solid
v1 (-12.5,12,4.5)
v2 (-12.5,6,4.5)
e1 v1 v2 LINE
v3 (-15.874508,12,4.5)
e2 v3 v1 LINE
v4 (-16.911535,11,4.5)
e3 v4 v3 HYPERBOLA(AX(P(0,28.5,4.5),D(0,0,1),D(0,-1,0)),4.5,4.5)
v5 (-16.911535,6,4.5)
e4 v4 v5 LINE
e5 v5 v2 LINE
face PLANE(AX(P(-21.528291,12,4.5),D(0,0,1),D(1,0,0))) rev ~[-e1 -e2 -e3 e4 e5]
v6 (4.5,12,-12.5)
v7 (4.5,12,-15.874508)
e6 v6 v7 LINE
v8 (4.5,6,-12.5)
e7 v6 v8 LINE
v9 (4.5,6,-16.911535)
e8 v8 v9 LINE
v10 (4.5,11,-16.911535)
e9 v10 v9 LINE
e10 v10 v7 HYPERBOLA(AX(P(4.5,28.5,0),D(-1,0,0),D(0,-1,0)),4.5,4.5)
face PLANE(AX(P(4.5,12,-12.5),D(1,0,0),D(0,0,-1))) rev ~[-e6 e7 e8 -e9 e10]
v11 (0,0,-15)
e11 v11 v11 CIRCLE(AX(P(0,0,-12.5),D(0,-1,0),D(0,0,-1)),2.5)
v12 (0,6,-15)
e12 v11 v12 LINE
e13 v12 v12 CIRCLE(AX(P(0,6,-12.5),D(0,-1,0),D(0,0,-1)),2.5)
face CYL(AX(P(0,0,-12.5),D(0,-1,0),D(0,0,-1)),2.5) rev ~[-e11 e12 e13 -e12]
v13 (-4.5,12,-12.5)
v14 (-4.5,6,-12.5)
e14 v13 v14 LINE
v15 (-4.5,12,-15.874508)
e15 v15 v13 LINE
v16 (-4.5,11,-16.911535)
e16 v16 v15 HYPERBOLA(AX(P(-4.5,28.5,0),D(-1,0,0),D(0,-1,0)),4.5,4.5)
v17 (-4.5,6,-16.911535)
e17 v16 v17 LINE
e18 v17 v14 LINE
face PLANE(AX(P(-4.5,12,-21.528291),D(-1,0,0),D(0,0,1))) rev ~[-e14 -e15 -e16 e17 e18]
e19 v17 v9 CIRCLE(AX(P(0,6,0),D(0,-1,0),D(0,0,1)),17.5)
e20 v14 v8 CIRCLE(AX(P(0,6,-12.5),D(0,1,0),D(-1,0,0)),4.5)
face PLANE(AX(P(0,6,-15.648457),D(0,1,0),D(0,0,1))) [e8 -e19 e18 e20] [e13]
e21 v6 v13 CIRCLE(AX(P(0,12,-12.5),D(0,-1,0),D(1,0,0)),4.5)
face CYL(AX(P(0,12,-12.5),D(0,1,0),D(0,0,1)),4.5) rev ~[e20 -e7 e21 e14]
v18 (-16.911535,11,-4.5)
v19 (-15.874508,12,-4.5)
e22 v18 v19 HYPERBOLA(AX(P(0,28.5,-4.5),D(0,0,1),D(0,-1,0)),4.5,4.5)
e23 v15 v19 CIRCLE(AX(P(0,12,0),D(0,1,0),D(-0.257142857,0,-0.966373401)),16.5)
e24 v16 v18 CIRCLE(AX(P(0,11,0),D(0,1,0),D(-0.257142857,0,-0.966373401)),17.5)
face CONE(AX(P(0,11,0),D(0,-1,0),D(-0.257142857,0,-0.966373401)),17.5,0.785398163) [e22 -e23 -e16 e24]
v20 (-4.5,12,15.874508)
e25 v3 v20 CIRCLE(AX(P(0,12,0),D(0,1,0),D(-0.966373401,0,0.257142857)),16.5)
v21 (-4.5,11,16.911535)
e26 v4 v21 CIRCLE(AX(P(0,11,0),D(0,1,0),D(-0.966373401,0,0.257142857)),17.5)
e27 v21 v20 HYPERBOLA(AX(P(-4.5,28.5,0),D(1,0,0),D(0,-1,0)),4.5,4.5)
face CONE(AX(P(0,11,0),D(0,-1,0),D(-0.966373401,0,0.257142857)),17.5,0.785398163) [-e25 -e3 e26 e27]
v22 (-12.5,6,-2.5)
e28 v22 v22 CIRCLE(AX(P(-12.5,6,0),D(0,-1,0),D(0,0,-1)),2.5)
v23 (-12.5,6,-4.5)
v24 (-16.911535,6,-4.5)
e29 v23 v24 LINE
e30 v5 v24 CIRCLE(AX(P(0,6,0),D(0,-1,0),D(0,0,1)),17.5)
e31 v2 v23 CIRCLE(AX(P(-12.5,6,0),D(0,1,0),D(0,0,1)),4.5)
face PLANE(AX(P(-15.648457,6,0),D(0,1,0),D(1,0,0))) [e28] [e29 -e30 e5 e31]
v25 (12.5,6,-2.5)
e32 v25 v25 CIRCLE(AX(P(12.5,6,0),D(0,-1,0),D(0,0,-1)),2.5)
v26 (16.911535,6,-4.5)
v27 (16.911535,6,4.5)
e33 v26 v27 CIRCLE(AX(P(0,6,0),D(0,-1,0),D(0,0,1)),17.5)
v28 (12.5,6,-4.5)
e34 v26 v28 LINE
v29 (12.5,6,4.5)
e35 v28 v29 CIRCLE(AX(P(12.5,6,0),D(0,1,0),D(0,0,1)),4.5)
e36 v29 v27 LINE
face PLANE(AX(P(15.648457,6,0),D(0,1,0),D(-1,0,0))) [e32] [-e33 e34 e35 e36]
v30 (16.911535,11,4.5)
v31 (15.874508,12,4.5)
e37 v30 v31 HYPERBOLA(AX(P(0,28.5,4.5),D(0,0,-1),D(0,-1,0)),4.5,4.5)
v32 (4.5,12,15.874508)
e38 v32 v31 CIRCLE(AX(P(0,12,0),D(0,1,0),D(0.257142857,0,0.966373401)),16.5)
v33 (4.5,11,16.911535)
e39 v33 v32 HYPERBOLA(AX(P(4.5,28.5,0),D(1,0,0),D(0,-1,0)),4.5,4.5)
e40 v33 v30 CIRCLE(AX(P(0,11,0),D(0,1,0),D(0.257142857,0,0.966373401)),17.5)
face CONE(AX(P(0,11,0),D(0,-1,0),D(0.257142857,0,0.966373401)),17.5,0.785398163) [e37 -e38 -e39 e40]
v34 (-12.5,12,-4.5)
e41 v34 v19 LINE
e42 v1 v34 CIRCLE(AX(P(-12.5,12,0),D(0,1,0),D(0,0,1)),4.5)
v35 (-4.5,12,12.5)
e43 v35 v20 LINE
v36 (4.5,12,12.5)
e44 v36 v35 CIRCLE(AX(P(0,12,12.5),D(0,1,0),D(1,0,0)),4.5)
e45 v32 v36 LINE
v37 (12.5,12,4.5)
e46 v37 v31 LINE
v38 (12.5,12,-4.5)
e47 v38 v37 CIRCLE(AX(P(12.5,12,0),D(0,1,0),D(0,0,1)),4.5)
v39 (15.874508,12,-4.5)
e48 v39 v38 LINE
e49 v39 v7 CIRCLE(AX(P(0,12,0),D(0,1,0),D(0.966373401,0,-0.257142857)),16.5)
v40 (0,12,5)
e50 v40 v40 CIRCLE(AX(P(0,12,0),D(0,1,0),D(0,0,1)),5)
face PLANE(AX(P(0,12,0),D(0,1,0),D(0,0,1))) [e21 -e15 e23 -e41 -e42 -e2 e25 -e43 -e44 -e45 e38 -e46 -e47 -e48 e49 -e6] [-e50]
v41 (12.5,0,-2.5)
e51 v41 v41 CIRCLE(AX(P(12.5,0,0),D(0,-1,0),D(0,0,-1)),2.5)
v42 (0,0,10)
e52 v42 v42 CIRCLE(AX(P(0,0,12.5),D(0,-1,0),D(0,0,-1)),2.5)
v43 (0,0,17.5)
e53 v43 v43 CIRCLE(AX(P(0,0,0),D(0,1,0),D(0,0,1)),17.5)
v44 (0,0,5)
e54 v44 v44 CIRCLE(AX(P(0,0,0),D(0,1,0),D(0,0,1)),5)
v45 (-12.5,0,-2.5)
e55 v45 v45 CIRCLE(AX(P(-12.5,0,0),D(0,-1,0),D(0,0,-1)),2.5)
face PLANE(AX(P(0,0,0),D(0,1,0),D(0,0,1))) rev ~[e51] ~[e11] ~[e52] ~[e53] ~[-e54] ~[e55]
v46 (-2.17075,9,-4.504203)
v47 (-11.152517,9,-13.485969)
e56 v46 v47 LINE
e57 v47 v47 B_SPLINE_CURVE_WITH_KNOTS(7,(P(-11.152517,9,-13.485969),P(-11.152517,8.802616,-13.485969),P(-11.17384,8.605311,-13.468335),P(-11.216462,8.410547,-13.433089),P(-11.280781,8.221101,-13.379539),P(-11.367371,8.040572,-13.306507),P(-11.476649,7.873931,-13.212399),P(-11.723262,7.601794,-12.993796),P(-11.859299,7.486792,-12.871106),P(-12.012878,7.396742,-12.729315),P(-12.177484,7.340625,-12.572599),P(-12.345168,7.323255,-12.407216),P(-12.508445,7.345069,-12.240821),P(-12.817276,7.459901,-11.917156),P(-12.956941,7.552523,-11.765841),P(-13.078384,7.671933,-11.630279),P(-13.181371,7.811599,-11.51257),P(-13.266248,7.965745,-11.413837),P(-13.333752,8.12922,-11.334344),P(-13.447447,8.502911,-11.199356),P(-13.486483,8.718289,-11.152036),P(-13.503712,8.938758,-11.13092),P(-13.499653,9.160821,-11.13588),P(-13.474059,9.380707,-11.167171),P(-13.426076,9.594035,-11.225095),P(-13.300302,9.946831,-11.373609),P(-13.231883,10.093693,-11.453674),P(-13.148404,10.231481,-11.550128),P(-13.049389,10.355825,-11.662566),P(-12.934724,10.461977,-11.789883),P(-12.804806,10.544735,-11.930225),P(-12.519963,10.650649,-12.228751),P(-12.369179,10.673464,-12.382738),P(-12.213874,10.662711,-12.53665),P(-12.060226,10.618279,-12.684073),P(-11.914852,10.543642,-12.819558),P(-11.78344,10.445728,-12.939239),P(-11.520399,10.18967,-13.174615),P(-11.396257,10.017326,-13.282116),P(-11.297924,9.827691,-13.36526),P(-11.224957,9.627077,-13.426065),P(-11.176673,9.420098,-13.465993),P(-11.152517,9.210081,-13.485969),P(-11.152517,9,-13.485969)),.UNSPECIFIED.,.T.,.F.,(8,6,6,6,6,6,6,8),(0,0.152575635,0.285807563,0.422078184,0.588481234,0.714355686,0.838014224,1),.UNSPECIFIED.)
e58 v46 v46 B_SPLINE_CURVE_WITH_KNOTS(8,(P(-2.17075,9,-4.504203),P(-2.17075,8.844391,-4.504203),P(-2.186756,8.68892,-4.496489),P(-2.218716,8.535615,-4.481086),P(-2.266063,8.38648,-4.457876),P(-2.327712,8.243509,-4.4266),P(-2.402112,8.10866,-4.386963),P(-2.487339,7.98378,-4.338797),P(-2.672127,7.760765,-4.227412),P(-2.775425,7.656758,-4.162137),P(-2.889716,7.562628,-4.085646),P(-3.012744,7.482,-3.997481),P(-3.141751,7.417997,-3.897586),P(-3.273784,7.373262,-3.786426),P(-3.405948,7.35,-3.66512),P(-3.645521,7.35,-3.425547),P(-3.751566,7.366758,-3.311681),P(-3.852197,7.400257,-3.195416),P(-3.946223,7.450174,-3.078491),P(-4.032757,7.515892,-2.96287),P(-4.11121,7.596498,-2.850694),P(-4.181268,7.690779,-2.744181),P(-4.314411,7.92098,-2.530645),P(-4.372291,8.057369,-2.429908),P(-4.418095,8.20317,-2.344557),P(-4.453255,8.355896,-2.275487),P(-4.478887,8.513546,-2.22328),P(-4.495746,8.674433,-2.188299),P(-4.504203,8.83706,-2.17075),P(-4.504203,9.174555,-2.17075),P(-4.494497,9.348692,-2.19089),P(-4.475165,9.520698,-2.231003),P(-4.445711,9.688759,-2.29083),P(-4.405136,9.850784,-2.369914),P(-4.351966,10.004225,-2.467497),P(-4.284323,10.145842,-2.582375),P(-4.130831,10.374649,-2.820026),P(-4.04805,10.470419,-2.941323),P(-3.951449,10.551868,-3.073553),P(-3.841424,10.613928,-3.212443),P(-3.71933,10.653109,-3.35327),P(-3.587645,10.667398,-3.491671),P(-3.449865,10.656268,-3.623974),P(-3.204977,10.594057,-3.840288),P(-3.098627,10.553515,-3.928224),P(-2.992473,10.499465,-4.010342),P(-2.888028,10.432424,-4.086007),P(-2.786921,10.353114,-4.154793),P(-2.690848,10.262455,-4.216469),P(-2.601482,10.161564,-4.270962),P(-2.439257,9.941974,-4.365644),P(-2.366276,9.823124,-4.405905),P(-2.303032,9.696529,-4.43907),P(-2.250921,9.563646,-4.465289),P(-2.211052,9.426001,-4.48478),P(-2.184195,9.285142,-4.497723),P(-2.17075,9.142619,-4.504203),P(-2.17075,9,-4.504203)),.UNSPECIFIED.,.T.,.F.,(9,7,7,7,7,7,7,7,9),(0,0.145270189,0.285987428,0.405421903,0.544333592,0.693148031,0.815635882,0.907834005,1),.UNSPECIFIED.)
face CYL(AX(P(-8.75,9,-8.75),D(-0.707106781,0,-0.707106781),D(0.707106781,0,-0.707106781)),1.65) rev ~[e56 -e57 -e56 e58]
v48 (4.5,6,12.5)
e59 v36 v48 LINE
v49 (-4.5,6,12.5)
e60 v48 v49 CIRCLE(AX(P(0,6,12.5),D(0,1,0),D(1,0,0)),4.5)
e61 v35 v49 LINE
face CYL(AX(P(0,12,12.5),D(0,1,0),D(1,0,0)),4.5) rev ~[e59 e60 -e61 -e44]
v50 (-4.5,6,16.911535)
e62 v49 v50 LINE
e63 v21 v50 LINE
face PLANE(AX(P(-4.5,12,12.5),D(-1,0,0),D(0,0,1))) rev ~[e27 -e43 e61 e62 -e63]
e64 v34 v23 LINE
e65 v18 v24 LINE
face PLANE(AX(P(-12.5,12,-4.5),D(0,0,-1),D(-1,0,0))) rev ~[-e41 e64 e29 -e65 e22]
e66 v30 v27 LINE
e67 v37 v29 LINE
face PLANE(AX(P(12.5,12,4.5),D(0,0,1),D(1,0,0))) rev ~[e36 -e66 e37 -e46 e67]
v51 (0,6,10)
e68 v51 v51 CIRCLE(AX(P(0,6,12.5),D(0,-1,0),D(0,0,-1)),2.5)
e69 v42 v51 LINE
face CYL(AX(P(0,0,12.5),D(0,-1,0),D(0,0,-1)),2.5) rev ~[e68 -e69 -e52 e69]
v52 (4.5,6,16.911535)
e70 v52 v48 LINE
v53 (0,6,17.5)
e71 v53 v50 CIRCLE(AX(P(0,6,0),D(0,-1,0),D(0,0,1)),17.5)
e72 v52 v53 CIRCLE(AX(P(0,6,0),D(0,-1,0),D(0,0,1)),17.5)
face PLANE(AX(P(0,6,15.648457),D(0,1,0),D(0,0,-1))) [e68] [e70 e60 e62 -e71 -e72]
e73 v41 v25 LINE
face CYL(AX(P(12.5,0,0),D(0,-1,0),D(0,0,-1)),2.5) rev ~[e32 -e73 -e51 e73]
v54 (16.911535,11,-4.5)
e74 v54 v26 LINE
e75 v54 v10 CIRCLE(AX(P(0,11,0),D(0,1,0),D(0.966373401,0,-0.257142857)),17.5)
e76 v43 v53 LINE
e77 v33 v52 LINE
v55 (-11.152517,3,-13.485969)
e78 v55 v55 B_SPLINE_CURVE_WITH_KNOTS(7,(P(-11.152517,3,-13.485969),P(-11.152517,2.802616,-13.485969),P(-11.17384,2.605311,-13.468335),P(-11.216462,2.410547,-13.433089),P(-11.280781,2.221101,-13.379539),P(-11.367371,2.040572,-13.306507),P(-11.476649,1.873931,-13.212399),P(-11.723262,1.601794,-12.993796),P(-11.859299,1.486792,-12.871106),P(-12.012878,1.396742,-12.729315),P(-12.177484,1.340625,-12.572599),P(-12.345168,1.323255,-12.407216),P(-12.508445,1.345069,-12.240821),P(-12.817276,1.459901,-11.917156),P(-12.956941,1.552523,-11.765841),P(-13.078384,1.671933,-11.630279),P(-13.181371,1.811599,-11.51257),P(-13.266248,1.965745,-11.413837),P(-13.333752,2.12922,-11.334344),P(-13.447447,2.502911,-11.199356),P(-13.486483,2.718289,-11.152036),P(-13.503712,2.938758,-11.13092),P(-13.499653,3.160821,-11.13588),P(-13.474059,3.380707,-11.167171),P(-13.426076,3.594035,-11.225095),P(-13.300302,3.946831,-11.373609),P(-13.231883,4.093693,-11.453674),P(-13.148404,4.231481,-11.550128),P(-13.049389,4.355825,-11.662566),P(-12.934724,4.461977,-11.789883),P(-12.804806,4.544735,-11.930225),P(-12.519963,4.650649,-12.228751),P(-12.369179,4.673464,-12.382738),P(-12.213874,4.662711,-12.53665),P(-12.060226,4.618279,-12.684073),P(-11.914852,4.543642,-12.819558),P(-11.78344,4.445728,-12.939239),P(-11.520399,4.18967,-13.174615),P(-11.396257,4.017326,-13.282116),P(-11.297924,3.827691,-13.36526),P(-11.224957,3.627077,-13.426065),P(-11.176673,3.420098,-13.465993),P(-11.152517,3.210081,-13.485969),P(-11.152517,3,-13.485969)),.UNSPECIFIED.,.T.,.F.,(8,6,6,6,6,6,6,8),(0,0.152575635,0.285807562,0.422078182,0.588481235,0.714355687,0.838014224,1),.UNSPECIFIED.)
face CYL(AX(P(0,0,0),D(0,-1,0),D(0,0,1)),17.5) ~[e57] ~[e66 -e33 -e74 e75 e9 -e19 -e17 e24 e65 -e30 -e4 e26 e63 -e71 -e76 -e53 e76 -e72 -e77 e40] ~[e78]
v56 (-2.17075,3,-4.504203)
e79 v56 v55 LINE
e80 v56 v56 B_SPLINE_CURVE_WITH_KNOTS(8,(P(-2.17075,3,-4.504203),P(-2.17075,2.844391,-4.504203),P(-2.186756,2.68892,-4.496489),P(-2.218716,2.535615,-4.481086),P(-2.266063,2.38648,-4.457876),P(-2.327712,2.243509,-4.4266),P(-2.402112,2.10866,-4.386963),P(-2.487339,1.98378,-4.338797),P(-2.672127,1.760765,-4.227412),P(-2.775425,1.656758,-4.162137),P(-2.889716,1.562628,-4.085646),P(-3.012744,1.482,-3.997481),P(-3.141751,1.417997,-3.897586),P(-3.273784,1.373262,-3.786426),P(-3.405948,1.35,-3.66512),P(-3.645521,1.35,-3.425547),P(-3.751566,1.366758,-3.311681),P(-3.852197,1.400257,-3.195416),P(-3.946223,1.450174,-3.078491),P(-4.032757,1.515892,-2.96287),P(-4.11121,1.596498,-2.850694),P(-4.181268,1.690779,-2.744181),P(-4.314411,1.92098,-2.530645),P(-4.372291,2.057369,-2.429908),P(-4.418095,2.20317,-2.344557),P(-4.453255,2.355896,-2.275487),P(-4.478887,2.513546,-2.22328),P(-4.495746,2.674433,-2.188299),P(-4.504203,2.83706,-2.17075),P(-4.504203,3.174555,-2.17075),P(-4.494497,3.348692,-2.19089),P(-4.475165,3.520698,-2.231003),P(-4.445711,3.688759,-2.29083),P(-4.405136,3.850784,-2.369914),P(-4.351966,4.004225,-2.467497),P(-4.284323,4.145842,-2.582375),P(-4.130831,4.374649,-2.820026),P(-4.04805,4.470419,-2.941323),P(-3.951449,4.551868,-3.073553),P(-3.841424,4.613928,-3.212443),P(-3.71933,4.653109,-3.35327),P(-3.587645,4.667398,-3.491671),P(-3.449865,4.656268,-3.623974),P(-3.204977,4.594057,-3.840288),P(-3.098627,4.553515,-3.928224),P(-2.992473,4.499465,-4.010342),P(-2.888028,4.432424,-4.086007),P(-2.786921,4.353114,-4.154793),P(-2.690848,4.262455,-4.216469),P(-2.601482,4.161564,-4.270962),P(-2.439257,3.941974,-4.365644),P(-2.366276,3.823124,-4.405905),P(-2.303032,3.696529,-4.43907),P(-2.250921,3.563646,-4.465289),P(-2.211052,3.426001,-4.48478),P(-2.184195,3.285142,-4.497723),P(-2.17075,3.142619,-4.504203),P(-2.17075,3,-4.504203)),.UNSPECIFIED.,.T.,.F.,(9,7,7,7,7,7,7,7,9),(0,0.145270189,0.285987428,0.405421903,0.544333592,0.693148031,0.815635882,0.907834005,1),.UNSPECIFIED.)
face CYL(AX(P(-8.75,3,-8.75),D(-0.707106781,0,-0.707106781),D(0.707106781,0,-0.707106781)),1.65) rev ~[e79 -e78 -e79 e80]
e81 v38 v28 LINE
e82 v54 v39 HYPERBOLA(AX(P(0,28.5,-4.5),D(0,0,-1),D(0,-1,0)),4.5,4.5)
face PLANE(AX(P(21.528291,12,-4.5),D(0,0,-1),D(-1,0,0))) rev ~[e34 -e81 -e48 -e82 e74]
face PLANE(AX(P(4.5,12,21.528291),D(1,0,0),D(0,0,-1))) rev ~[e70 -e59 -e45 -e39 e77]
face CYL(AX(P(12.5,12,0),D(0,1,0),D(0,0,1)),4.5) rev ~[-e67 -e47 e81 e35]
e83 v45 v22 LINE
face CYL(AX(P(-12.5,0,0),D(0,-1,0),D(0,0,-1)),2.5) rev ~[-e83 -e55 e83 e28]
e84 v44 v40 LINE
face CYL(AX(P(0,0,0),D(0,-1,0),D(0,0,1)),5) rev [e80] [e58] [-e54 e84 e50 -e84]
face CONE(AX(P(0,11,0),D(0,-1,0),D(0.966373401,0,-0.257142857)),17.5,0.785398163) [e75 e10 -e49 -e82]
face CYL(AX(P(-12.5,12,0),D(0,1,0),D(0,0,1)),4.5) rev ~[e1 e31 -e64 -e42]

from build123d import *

# Parameters (mm, degrees)
SKETCH1_R                  = 17.5
SKETCH1_R_2                = 5
BOSS_EXTRUDE1_DEPTH        = 12
SKETCH4_R                  = 2.5
CUT_EXTRUDE2_DEPTH         = 28.504545079
SKETCH7_R                  = 4.5
CUT_EXTRUDE4_DEPTH         = 6
CUT_EXTRUDE5_DEPTH         = 6
CIRPATTERN1_COUNT          = 4
SKETCH9_W                  = 1.65
SKETCH9_H                  = 24.748737342
M4_TAPPED_HOLE1_AT_2_COUNT = 2
M4_TAPPED_HOLE1_AT_2_PITCH = 6
CHAMFER1_SIZE              = 1


with BuildPart() as part:
    # Sketch1 → Boss-Extrude1 (new body)
    with BuildSketch(Plane(origin=(0, 0, 0), x_dir=(1, 0, 0), z_dir=(0, 1, 0))):
        with Locations(Location((0, 0, 0), (0, 0, 270))):
            Circle(SKETCH1_R)
        with Locations(Location((0, 0, 0), (0, 0, 270))):
            Circle(SKETCH1_R_2, mode=Mode.SUBTRACT)
    extrude(amount=BOSS_EXTRUDE1_DEPTH)

    # Sketch4 → Cut-Extrude2 (cut, through all)
    with BuildSketch(Plane.XZ):
        with Locations(Location((0, 12.5, 0), (0, 0, 270))):
            Circle(SKETCH4_R)
        with Locations(Location((-12.5, 0, 0), (0, 0, 270))):
            Circle(SKETCH4_R)
        with Locations(Location((12.5, 0, 0), (0, 0, 270))):
            Circle(SKETCH4_R)
        with Locations(Location((0, -12.5, 0), (0, 0, 270))):
            Circle(SKETCH4_R)
    extrude(amount=-CUT_EXTRUDE2_DEPTH, mode=Mode.SUBTRACT)

    # Sketch7 → Cut-Extrude4 (cut)
    with BuildSketch(Plane(origin=(0, 12, 0), x_dir=(1, 0, 0), z_dir=(0, 1, 0))):
        with Locations(Location((0, 12.5, 0), (0, 0, 270))):
            Circle(SKETCH7_R)
        with Locations(Location((12.5, 0, 0), (0, 0, 270))):
            Circle(SKETCH7_R)
        with Locations(Location((0, -12.5, 0), (0, 0, 270))):
            Circle(SKETCH7_R)
        with Locations(Location((-12.5, 0, 0), (0, 0, 270))):
            Circle(SKETCH7_R)
    extrude(amount=-CUT_EXTRUDE4_DEPTH, mode=Mode.SUBTRACT)

    # Sketch8 → Cut-Extrude5 (cut)
    with BuildSketch(Plane(origin=(0, 12, 0), x_dir=(1, 0, 0), z_dir=(0, 1, 0))):
        with BuildLine():
            Line((-12.5, 4.5), (-21.528291401, 4.5))
            Line((-21.528291401, 4.5), (-21.528291401, -4.5))
            Line((-21.528291401, -4.5), (-12.5, -4.5))
            ThreePointArc((-12.5, -4.5), (-8, 0), (-12.5, 4.5))
        make_face()
    cut_extrude5 = extrude(amount=-CUT_EXTRUDE5_DEPTH, mode=Mode.SUBTRACT)

    # CirPattern1: Cut-Extrude5 ×4 about axis
    cirpattern1_axis = Axis((0, 0, 0), (0, 1, 0))
    for i in range(1, CIRPATTERN1_COUNT):
        add(cut_extrude5.rotate(cirpattern1_axis, i * 360 / CIRPATTERN1_COUNT), mode=Mode.SUBTRACT)

    # Sketch9 → M4 Tapped Hole1 (revolve, cut)
    with BuildSketch(Plane(origin=(0, 3, 0), x_dir=(0.7071067811865464, 0, -0.7071067811865488), z_dir=(0, 1, 0))):
        with Locations((0.825, 12.374368671)):
            Rectangle(SKETCH9_W, SKETCH9_H)
    m4_tapped_hole1 = revolve(axis=Axis((4.490128061, 3, 4.490128061), (-0.7071067811865487, 0, -0.7071067811865464)), mode=Mode.SUBTRACT)

    # M4 Tapped Hole1 at 2: M4 Tapped Hole1 ×2
    with Locations(*[(0, i * M4_TAPPED_HOLE1_AT_2_PITCH, 0) for i in range(1, M4_TAPPED_HOLE1_AT_2_COUNT)]):
        add(m4_tapped_hole1, mode=Mode.SUBTRACT)

    # Chamfer1
    chamfer1_edges = [part.edges().sort_by_distance(p)[0] for p in [
        (12.374368671, 12, 12.374368671),
        (-12.374368671, 12, 12.374368671),
        (-12.374368671, 12, -12.374368671),
        (12.374368671, 12, -12.374368671),
    ]]
    chamfer(chamfer1_edges, length=CHAMFER1_SIZE)


solid = part.part
